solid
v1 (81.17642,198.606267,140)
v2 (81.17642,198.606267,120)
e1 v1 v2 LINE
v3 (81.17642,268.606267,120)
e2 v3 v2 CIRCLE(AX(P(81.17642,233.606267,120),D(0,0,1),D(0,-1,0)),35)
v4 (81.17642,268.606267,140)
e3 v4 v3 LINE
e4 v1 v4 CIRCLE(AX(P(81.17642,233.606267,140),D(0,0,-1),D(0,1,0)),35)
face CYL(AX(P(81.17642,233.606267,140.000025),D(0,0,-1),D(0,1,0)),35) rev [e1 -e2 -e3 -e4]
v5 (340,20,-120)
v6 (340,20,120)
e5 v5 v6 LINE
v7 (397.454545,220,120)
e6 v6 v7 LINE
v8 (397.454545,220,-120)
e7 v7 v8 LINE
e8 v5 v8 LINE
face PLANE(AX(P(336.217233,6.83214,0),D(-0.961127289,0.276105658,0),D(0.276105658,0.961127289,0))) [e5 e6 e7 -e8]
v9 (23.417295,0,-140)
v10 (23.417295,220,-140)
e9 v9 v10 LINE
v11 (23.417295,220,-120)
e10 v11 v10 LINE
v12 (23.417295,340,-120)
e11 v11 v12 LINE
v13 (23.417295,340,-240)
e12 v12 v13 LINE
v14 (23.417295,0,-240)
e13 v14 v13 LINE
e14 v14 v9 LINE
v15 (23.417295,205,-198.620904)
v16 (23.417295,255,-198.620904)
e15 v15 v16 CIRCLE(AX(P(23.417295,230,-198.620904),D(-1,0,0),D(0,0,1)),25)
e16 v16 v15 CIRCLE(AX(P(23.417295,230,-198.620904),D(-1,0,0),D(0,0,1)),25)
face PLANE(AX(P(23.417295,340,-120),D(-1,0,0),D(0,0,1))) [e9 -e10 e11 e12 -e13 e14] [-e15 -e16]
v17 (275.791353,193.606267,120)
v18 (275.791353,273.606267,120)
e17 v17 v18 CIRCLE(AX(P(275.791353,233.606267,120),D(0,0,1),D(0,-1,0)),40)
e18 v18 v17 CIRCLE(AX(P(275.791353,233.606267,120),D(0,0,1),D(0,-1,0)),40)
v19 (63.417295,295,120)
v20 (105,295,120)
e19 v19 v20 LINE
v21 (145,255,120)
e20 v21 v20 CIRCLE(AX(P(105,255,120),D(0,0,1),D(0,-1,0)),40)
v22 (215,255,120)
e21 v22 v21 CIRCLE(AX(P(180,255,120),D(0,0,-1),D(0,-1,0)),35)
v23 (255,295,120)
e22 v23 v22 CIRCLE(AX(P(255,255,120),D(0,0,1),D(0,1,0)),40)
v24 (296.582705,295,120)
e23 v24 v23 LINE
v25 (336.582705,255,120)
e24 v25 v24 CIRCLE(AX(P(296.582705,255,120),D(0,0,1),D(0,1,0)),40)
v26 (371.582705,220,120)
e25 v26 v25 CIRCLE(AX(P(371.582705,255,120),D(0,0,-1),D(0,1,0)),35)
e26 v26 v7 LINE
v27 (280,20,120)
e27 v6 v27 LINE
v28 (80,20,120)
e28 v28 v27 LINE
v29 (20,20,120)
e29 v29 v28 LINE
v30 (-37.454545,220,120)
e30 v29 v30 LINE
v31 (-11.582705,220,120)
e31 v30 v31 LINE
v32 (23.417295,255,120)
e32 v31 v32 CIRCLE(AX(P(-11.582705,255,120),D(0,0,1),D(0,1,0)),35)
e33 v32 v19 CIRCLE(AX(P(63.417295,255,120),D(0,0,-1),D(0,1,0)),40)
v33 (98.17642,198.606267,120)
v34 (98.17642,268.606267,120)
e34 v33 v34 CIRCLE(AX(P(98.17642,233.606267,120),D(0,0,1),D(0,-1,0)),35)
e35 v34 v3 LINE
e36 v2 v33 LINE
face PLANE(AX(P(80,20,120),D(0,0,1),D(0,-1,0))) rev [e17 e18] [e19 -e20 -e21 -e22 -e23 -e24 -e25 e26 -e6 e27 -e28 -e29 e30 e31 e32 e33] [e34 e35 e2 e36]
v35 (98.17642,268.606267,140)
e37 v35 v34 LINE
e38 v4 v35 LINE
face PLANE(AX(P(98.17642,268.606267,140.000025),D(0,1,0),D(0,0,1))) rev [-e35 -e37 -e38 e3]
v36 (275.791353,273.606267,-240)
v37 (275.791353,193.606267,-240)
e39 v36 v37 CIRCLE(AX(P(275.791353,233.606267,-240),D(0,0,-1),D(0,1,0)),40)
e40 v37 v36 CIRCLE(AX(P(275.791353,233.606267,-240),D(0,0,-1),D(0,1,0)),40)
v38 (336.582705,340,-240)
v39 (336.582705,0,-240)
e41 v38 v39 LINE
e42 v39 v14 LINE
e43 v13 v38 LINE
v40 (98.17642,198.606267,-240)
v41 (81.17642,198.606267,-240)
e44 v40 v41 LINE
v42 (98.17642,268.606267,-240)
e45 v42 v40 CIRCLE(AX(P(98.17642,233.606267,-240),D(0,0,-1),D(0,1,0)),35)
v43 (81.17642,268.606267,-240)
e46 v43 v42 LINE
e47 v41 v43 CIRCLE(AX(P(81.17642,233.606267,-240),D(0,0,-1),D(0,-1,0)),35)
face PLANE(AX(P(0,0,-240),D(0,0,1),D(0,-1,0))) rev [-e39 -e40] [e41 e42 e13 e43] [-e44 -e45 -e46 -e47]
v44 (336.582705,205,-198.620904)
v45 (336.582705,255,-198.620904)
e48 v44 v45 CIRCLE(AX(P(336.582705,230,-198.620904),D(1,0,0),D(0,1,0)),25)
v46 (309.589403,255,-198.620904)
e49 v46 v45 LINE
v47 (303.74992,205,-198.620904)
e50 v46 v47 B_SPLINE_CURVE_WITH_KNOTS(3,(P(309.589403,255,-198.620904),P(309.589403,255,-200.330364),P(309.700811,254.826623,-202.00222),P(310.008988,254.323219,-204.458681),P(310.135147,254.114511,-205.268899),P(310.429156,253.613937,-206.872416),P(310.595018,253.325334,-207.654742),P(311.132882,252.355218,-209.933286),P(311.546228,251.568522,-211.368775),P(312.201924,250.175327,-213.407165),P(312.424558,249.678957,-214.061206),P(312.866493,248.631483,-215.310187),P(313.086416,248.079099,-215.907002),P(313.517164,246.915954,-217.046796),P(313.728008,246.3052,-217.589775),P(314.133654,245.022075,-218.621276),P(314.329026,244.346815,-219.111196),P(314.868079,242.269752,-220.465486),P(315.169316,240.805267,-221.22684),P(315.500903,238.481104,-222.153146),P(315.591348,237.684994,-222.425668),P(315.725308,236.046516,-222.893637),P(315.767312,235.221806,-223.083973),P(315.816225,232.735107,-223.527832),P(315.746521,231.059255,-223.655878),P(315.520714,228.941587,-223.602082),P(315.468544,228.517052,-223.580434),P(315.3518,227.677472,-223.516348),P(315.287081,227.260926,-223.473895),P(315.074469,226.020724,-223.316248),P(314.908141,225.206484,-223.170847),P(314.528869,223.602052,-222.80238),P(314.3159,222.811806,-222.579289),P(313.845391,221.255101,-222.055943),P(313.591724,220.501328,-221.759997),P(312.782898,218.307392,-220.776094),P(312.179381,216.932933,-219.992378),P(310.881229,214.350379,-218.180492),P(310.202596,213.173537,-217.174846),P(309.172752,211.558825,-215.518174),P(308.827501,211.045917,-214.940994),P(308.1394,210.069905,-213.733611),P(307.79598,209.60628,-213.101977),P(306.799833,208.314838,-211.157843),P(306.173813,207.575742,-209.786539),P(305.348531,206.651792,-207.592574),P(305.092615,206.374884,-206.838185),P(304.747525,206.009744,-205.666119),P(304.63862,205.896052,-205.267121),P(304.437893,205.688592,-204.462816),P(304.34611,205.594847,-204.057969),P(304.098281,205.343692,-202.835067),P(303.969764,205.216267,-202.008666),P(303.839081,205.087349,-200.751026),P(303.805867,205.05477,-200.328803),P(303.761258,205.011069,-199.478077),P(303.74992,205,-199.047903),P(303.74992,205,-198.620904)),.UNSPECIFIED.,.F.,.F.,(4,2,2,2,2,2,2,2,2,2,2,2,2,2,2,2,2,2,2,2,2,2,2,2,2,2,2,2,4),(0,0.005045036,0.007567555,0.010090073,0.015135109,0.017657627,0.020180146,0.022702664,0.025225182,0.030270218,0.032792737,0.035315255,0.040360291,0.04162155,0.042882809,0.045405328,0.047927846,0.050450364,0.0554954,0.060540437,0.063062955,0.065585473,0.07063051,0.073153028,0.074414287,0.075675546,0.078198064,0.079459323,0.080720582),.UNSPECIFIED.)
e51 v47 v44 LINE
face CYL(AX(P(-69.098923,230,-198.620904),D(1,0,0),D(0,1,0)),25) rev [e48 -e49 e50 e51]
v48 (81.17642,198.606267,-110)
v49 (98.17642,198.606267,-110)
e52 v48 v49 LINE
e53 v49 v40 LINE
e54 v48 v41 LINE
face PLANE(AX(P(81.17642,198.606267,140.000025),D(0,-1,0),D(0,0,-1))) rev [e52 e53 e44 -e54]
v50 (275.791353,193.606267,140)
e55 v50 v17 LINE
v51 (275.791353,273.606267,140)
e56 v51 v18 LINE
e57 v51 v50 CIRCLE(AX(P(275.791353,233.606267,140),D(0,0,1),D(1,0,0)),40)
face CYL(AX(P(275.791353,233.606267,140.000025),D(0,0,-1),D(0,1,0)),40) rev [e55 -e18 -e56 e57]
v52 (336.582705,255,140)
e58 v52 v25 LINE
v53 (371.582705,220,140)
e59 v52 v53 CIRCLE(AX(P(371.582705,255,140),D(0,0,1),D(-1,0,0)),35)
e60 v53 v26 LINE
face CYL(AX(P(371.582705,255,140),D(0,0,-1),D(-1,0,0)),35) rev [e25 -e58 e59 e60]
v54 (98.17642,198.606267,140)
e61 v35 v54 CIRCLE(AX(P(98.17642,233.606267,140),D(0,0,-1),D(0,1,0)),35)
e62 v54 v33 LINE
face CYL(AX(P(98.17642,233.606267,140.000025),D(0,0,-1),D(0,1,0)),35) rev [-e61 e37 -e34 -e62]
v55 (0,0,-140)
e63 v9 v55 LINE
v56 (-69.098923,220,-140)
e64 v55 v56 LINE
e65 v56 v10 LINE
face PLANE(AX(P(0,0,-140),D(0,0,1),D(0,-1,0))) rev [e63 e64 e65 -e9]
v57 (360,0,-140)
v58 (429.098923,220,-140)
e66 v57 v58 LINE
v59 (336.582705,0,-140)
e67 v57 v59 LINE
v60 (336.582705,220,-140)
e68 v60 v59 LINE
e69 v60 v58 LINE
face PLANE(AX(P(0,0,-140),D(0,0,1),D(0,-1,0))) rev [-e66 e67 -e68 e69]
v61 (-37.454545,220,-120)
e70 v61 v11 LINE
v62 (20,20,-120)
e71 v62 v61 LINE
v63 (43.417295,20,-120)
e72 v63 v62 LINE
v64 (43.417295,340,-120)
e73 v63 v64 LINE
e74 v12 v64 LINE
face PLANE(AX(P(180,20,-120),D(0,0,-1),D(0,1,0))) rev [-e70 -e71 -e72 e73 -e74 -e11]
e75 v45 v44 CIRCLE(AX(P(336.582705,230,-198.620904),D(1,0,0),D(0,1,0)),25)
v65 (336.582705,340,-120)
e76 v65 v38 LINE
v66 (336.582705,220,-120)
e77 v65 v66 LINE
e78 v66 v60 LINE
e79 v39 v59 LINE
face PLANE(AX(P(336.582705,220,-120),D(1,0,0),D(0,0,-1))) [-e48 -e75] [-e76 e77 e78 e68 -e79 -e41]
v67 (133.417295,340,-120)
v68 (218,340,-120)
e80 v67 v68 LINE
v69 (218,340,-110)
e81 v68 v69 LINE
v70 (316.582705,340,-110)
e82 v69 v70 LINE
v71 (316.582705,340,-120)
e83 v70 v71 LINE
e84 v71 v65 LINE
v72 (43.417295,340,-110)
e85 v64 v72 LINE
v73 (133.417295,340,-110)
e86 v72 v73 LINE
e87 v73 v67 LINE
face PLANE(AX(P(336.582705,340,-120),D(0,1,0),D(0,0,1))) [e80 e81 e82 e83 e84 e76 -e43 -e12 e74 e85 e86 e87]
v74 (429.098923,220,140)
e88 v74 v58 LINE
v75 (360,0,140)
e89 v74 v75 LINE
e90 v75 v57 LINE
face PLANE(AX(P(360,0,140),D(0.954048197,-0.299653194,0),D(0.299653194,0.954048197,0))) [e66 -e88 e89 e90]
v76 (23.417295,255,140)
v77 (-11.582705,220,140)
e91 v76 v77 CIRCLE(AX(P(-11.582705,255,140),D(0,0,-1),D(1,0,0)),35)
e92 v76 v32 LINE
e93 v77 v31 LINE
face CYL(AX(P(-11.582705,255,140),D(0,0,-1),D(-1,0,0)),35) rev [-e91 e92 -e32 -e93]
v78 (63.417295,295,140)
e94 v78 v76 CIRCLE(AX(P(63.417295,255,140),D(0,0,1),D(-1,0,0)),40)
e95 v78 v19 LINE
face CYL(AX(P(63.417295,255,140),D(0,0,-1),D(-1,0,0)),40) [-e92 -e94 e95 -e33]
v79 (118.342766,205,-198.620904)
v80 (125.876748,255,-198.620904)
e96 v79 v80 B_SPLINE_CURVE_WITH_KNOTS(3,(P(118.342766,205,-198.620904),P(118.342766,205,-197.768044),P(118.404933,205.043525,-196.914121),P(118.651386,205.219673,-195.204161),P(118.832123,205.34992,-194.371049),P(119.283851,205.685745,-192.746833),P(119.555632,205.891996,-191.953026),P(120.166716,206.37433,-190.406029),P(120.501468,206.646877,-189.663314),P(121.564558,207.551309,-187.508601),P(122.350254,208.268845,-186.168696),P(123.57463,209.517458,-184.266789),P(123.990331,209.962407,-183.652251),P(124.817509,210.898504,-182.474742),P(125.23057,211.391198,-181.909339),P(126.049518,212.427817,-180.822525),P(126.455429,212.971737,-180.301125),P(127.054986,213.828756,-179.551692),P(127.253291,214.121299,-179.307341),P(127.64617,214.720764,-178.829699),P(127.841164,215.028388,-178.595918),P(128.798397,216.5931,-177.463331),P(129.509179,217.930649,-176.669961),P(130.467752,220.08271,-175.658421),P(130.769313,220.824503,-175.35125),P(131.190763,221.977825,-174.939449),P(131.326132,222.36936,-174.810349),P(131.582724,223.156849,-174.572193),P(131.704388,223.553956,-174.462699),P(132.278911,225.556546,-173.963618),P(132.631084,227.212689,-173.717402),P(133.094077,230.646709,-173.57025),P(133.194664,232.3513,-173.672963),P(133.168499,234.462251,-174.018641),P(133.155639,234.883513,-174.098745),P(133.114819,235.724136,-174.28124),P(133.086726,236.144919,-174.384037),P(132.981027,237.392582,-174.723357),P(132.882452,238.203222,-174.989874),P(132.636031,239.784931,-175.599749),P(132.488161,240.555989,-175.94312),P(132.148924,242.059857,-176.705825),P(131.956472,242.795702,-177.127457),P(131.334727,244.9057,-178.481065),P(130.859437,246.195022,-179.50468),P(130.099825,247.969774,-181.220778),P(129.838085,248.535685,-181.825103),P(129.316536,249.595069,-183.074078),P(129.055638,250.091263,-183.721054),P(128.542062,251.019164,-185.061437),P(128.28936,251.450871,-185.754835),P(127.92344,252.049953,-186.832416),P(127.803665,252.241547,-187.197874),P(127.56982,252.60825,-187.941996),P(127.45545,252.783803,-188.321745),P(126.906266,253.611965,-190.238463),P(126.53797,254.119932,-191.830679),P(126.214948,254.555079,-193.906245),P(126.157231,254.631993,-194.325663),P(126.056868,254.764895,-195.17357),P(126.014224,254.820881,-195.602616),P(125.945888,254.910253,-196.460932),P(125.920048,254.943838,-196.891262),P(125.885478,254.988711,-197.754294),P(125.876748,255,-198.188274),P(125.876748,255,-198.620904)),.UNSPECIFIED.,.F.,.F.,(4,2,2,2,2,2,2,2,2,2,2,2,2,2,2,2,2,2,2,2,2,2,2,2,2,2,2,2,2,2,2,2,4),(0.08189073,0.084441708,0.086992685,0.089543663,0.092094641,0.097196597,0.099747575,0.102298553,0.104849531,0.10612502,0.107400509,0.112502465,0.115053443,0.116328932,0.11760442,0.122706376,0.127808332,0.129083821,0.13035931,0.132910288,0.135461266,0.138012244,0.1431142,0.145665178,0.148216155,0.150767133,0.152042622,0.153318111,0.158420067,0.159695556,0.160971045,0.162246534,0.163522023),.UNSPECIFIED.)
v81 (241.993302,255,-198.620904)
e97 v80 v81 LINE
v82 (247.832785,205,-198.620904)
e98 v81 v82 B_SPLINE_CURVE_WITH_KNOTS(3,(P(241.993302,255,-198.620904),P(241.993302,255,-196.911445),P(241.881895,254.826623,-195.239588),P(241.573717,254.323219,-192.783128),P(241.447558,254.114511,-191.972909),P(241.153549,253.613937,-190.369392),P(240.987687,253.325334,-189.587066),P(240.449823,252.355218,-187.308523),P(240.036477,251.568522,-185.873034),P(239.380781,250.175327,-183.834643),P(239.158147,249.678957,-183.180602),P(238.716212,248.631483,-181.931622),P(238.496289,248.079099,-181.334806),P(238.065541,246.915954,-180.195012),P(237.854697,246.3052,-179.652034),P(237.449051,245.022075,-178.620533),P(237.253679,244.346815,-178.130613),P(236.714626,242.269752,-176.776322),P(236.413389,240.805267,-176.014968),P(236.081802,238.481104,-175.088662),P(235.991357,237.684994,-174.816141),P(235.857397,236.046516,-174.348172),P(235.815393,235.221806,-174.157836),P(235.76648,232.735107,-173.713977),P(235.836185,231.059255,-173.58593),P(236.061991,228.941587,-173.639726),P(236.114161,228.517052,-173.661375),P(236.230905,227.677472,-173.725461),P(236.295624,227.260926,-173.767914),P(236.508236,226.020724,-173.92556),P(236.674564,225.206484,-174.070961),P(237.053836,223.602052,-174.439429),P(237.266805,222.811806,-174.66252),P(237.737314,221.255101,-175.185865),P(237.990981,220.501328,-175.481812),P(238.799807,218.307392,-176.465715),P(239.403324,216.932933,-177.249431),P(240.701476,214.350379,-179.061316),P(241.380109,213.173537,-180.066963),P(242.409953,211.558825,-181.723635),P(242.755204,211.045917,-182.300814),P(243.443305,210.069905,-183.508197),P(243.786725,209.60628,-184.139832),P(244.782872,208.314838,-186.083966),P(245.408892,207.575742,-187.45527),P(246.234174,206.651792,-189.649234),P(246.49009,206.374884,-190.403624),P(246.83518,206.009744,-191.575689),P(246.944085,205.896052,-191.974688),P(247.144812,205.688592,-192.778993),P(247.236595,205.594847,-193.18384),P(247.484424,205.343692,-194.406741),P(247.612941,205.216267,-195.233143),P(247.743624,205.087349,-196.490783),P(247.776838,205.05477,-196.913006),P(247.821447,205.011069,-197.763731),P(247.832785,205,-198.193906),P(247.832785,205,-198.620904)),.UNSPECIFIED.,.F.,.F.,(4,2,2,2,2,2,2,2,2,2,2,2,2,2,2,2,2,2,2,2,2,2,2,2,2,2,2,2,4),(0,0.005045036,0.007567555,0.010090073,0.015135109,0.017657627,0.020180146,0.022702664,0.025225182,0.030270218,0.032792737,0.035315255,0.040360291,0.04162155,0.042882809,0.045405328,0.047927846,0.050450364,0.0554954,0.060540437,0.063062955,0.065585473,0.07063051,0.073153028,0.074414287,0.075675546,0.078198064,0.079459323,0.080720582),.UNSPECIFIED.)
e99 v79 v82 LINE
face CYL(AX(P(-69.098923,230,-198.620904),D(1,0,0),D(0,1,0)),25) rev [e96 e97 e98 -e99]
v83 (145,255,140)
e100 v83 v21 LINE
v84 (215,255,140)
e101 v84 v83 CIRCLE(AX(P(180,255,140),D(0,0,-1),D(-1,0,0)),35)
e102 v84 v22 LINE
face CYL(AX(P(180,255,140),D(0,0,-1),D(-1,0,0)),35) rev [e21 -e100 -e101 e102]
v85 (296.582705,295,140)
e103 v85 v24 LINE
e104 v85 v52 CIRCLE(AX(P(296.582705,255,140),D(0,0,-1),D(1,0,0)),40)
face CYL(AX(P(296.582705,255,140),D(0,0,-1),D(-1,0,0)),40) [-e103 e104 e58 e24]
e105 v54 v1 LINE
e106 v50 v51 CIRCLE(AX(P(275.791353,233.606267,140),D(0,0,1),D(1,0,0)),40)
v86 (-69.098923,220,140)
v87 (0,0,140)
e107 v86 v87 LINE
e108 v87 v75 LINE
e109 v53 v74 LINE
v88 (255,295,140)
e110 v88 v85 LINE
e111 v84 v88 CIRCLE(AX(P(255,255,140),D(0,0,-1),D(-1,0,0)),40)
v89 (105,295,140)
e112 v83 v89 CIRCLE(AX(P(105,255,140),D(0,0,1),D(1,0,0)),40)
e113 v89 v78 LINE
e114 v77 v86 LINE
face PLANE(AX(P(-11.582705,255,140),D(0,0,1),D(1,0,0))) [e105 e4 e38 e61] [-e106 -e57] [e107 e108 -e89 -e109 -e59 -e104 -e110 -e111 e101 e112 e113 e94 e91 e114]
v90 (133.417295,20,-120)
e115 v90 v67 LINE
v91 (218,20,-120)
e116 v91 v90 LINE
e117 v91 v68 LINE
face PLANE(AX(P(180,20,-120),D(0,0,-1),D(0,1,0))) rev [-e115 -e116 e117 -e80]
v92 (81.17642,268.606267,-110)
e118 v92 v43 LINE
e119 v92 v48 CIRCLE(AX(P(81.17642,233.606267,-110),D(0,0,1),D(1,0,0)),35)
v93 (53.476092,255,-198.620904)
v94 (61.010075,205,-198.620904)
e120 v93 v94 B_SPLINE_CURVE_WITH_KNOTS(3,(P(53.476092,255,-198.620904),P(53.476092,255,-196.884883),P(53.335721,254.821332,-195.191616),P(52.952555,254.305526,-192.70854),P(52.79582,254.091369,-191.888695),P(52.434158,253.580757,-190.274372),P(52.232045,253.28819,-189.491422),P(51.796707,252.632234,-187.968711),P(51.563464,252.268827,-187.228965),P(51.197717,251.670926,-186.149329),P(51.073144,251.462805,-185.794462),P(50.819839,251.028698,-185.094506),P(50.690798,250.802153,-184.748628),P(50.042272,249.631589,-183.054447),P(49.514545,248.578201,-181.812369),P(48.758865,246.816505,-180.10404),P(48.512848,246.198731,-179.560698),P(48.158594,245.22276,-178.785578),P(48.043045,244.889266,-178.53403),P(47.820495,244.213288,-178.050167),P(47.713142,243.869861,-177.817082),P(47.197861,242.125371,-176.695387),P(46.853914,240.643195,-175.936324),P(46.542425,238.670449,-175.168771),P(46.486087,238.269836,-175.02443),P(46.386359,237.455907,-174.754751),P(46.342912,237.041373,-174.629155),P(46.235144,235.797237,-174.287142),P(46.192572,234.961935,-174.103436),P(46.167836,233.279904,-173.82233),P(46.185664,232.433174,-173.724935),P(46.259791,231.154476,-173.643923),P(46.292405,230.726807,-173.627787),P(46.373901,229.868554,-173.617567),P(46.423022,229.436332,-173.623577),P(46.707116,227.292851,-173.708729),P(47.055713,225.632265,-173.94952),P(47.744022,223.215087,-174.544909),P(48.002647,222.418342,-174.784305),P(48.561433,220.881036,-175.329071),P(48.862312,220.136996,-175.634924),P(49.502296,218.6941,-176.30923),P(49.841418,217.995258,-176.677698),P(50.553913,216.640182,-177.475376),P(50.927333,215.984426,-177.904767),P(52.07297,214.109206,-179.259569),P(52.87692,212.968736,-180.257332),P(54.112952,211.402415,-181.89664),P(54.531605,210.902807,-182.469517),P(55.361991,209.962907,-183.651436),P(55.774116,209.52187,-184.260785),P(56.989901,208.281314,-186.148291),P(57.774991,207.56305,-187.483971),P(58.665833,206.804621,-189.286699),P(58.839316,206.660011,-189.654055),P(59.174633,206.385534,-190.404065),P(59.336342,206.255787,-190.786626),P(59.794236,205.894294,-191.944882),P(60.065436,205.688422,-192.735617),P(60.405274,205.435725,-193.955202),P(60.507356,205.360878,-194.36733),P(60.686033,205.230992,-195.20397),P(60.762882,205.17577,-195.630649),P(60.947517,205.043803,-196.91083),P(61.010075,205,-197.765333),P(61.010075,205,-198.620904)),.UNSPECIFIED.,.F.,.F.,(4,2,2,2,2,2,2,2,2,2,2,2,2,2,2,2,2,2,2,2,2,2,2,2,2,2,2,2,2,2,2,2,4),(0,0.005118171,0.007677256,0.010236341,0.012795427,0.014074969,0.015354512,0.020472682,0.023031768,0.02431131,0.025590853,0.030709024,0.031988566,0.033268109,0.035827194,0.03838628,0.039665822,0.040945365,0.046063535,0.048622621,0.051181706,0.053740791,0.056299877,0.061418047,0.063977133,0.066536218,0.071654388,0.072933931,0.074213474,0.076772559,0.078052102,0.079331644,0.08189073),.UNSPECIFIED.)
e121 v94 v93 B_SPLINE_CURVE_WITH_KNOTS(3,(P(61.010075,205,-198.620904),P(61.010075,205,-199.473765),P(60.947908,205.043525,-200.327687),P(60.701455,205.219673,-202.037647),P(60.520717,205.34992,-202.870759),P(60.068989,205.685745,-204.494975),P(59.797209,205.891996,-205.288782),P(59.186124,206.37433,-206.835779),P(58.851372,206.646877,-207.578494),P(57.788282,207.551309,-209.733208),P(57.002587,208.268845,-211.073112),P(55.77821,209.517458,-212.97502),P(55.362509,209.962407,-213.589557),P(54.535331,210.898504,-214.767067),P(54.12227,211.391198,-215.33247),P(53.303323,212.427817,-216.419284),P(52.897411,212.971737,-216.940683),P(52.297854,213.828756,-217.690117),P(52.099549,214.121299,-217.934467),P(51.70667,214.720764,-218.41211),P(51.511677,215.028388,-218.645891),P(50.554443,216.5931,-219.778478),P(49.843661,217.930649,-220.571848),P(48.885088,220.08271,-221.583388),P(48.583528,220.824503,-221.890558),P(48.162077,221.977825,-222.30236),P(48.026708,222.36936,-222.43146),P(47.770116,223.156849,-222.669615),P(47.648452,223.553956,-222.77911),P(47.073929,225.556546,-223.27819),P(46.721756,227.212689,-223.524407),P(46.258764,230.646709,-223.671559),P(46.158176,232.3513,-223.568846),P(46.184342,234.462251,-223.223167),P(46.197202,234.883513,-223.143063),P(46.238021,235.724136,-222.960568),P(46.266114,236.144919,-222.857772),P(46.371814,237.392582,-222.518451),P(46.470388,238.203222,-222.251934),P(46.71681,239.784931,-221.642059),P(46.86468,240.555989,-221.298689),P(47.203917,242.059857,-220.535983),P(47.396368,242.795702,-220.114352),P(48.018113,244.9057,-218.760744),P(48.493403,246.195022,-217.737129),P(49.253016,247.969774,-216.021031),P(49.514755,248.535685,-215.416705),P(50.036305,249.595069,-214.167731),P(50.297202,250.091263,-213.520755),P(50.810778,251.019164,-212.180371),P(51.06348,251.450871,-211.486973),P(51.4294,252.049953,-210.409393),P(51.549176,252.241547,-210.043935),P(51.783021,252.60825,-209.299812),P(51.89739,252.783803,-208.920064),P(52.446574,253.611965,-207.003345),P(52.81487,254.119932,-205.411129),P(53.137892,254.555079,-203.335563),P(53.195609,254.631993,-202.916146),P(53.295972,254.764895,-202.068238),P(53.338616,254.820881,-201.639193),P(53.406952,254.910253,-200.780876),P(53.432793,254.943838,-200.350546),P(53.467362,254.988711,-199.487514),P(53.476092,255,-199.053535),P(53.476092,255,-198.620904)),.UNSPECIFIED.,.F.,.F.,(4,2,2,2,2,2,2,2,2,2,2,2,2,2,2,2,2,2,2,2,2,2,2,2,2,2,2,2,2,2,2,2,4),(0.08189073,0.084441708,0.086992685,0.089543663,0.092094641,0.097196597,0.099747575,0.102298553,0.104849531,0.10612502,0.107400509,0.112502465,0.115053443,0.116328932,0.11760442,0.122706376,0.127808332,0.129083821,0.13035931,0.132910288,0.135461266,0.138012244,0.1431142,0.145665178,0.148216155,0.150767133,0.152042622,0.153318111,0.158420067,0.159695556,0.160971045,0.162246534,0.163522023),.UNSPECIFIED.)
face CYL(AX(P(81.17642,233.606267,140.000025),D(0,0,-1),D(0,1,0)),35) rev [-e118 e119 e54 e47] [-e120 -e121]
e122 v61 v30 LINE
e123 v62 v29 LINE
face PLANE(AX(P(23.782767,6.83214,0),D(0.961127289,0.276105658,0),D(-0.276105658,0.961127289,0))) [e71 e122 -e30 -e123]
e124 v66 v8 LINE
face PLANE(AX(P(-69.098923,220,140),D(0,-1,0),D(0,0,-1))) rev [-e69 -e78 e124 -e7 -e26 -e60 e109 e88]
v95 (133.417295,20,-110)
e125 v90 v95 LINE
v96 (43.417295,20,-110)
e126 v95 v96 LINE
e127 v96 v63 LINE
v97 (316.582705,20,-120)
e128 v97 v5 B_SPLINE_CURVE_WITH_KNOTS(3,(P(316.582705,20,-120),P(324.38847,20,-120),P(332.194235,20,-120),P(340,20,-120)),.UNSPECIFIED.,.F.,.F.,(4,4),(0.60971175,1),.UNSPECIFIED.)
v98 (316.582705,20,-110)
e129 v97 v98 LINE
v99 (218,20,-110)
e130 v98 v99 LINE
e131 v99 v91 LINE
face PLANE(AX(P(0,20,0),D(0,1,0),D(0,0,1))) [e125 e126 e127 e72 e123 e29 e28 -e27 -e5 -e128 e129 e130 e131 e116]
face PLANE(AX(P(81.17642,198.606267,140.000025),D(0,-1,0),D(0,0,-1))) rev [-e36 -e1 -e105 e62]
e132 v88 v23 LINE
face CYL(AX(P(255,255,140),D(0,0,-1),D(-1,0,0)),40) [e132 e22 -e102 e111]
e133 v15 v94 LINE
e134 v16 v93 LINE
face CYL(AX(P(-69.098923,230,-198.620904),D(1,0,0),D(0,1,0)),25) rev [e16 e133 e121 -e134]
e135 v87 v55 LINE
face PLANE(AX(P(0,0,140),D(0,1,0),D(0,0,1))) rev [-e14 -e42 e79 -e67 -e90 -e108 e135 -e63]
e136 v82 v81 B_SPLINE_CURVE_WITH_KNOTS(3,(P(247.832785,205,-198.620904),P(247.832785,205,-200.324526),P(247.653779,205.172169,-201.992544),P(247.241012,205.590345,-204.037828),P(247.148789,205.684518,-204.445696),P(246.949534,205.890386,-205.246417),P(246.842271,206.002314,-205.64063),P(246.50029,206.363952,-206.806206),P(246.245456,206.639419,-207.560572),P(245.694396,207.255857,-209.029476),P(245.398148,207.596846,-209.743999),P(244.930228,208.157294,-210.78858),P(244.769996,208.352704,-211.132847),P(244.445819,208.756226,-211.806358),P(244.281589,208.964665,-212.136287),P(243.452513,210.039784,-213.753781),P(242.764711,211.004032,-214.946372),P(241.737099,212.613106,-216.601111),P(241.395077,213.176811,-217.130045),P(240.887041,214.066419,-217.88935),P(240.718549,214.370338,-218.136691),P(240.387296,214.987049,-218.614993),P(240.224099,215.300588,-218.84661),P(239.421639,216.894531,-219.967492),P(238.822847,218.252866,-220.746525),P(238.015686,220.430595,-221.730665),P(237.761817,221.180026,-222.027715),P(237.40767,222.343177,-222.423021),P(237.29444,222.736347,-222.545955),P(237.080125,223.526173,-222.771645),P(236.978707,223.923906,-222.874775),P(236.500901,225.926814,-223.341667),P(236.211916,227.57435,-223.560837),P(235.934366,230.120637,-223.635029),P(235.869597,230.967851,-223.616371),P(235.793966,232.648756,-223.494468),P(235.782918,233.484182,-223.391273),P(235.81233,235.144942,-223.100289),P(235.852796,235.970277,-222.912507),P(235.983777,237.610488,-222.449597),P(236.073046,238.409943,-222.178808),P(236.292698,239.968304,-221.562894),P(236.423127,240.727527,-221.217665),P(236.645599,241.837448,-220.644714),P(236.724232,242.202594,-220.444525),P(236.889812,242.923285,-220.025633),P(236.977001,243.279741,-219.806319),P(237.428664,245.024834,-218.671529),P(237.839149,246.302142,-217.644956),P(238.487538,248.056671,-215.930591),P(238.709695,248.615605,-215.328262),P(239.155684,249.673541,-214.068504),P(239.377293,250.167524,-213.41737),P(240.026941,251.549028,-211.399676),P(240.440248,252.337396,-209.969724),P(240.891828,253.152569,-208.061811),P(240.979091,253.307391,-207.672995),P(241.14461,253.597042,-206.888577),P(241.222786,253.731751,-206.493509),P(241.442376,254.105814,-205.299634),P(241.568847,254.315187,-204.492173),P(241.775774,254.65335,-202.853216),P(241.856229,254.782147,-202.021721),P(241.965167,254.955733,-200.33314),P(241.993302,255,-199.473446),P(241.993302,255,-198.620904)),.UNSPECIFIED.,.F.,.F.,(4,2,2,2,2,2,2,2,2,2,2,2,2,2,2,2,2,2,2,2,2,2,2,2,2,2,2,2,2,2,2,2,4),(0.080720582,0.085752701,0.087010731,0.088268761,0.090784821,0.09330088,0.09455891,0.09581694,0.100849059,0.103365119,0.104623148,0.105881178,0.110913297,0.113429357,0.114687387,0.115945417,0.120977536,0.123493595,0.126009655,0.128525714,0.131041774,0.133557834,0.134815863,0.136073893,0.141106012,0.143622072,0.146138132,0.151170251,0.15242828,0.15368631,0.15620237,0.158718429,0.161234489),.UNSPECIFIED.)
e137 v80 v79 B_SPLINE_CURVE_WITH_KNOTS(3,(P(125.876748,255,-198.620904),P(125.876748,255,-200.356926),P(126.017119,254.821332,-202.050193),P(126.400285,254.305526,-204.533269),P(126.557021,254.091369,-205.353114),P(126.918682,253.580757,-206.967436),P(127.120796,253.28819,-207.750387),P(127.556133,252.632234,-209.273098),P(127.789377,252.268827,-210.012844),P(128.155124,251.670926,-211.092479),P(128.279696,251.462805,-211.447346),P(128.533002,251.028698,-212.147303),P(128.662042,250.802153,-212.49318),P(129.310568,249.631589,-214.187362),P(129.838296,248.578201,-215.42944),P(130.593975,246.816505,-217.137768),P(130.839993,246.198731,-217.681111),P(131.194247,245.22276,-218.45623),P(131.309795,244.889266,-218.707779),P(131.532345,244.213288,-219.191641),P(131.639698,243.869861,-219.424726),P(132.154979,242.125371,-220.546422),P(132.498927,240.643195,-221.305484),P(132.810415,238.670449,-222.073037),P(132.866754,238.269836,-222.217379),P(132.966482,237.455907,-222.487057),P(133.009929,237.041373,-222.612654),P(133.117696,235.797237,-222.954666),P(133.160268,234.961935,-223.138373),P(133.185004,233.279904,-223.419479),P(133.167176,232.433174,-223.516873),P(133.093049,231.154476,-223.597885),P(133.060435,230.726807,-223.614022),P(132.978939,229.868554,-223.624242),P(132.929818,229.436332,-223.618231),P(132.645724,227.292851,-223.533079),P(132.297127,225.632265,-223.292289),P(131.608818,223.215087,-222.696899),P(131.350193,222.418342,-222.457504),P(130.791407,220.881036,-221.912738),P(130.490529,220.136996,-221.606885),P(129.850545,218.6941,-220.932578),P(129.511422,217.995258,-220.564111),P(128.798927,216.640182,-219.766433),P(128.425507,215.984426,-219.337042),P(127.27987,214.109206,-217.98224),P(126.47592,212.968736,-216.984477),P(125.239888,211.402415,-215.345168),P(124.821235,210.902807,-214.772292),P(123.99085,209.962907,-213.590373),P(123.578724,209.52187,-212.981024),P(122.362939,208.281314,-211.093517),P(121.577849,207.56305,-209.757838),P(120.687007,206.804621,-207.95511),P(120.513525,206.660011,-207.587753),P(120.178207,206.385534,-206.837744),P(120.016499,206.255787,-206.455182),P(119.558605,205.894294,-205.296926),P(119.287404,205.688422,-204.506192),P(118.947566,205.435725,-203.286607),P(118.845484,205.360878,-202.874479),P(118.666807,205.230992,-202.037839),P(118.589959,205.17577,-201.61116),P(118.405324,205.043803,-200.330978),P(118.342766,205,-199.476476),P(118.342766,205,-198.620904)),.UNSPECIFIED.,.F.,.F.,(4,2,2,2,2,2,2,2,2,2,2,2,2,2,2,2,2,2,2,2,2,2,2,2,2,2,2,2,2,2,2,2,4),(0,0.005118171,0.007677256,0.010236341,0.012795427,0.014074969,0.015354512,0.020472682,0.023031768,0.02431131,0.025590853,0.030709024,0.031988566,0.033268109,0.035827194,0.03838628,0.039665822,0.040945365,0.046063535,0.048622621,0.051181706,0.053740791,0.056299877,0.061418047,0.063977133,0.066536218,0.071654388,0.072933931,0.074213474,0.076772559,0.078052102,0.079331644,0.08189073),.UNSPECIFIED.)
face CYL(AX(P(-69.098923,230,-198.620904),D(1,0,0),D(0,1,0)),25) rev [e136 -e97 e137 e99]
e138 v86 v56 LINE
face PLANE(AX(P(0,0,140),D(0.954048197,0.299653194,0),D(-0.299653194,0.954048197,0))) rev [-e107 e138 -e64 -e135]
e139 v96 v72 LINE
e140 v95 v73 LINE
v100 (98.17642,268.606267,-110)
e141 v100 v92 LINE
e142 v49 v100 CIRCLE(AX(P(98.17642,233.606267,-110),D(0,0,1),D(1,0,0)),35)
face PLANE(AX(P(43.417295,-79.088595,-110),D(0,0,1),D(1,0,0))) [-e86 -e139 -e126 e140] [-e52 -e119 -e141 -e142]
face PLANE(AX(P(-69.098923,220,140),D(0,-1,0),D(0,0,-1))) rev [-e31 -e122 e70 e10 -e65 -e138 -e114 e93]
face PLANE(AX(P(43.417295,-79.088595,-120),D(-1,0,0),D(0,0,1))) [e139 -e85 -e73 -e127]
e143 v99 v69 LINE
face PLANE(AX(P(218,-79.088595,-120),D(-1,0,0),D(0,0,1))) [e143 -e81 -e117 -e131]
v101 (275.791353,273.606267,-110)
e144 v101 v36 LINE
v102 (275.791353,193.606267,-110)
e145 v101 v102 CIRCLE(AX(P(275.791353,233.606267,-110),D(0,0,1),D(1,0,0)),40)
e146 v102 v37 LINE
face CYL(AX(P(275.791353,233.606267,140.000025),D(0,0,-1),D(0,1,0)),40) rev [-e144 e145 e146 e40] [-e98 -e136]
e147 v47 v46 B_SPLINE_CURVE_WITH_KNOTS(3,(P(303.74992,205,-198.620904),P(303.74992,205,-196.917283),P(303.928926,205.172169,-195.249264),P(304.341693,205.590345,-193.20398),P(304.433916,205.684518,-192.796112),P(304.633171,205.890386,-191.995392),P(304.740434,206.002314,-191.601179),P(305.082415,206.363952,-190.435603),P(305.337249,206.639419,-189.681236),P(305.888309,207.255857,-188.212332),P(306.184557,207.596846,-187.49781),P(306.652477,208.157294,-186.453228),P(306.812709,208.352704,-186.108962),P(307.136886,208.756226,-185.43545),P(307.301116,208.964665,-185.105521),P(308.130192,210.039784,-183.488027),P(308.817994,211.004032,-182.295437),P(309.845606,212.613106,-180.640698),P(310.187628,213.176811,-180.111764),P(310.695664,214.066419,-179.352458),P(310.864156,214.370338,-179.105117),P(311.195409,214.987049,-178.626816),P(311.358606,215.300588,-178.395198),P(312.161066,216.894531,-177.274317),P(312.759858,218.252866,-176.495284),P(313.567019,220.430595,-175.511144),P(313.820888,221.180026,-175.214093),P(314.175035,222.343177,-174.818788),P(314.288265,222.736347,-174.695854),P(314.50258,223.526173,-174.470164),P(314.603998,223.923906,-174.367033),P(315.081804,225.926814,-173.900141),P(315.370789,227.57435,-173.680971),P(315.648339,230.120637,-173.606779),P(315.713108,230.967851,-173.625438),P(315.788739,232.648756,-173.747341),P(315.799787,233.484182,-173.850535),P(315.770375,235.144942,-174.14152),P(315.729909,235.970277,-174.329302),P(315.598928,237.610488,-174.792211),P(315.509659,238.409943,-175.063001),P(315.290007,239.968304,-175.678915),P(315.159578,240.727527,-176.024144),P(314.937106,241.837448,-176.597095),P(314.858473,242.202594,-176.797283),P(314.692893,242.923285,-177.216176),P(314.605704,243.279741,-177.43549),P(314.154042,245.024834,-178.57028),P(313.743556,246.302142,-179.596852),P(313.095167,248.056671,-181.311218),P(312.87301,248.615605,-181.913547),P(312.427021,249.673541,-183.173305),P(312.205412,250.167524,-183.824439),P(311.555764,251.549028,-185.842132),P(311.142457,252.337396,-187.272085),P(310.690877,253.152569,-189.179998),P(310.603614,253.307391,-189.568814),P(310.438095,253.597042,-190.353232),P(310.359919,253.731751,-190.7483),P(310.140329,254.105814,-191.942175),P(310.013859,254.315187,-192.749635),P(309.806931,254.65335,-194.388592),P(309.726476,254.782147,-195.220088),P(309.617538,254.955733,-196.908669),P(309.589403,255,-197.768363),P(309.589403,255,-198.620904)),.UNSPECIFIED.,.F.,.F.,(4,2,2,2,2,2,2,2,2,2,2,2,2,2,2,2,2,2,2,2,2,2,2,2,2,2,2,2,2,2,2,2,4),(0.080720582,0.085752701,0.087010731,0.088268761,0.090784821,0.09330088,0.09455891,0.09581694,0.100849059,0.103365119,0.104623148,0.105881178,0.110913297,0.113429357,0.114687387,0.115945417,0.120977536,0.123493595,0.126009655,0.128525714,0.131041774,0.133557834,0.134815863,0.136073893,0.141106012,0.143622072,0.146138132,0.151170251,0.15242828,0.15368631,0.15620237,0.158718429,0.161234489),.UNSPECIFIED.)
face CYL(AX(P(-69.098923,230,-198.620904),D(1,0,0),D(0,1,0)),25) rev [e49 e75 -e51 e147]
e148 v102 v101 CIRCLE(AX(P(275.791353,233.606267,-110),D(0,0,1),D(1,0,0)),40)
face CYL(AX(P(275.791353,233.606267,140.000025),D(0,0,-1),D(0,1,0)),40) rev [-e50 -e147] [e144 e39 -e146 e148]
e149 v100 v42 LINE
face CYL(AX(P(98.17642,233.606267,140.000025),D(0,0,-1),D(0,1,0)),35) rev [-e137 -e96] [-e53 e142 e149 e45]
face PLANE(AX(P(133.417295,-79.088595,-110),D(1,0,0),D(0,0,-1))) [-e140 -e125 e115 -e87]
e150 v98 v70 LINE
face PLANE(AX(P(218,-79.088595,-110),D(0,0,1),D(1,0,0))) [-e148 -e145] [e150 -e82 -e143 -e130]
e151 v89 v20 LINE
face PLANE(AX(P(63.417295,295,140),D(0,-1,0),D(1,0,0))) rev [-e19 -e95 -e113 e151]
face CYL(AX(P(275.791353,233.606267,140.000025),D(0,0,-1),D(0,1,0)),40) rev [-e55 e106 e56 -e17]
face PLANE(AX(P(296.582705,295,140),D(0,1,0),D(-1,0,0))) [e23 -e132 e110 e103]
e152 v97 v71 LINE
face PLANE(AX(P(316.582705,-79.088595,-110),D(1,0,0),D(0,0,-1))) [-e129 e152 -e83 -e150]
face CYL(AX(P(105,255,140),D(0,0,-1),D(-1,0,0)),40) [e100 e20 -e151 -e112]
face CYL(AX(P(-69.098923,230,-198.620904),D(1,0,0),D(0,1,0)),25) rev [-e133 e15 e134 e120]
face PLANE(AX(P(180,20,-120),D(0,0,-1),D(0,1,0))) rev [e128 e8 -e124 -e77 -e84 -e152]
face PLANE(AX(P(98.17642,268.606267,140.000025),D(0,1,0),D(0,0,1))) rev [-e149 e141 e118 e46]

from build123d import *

# Parameters (mm, degrees)
EXTRUDE_2_DEPTH          = 140
EXTRUDE_3_DEPTH          = 140
SKETCH_8_W               = 100
SKETCH_8_H               = 240
CUT_EXTRUDE_1_DEPTH      = 275
EXTRUDE_4_DEPTH          = 100
EXTRUDE_4_DEPTH_BACK     = 20
SKETCH_12_W              = 313.16541006
SKETCH_12_H              = 120
SKETCH_13_W              = 313.16541006
SKETCH_13_H              = 220
EXTRUDE_5_DEPTH          = 100
SKETCH_14_R              = 25
CUT_EXTRUDE_2_DEPTH      = 582.186358517
SKETCH_15_W              = 90
SKETCH_15_H              = 10
SKETCH_15_W_2            = 98.58270503
EXTRUDE_6_DEPTH          = 320
CUT_EXTRUDE_3_DEPTH      = 615.919414052
CUT_EXTRUDE_3_DEPTH_BACK = 615.919414052
SKETCH_16_R              = 40


with BuildPart() as part:
    # 草图1 → 凸台-拉伸2 (new body)
    with BuildSketch(Plane.XY):
        with BuildLine():
            Line((0, 0), (180, 0))
            Line((180, 0), (180, 220))
            ThreePointArc((180, 220), (155.251262658, 230.251262658), (145, 255))
            ThreePointArc((145, 255), (133.284271247, 283.284271247), (105, 295))
            Line((105, 295), (63.41729497, 295))
            ThreePointArc((63.41729497, 295), (35.133023723, 283.284271247), (23.41729497, 255))
            ThreePointArc((23.41729497, 255), (13.166032312, 230.251262658), (-11.58270503, 220))
            Line((-11.58270503, 220), (-69.098922823, 220))
            Line((-69.098922823, 220), (0, 0))
        make_face()
    extrude_2 = extrude(amount=EXTRUDE_2_DEPTH)

    # 草图5 → 凸台-拉伸3 (add)
    with BuildSketch(Plane(origin=(0, 0, 0), x_dir=(-1, 0, 0), z_dir=(0, 0, -1))):
        Polygon((-180, 220), (69.098922823, 220), (0, 0), (-180, 0), align=None)
    extrude_3 = extrude(amount=EXTRUDE_3_DEPTH)

    # 草图8 → 切除-拉伸1 (cut)
    with BuildSketch(Plane(origin=(0, 295, 0), x_dir=(1, 0, 0), z_dir=(0, 1, 0))):
        with Locations((130, 0)):
            Rectangle(SKETCH_8_W, SKETCH_8_H)
    cut_extrude_1 = extrude(amount=-CUT_EXTRUDE_1_DEPTH, mode=Mode.SUBTRACT)

    # 草图10 → 切除-放样4 section 0
    with BuildSketch(Plane(origin=(0, 20, 0), x_dir=(1, 0, 0), z_dir=(0, 1, 0))):
        with BuildLine():
            Line((80, 120), (20, 120))
            Line((20, 120), (20, -120))
            Line((20, -120), (80, -120))
            Line((80, -120), (80, 120))
        make_face()
    # 草图11 → 切除-放样4 section 1
    with BuildSketch(Plane(origin=(0, 295, 0), x_dir=(1, 0, 0), z_dir=(0, 1, 0))):
        with BuildLine():
            Line((80, 120), (80, -120))
            Line((80, -120), (-59, -120))
            Line((-59, -120), (-59, 120))
            Line((-59, 120), (80, 120))
        make_face()
    loft_4 = loft(mode=Mode.SUBTRACT)

    # 镜向1: 凸台-拉伸2, 凸台-拉伸3, 切除-拉伸1, 切除-放样4 across plane
    add(extrude_2.mirror(Plane(origin=(180, 0, 140), x_dir=(0, 0, 1), z_dir=(-1, 0, 0))))
    add(extrude_3.mirror(Plane(origin=(180, 0, 140), x_dir=(0, 0, 1), z_dir=(-1, 0, 0))))
    add(cut_extrude_1.mirror(Plane(origin=(180, 0, 140), x_dir=(0, 0, 1), z_dir=(-1, 0, 0))), mode=Mode.SUBTRACT)
    add(loft_4.mirror(Plane(origin=(180, 0, 140), x_dir=(0, 0, 1), z_dir=(-1, 0, 0))), mode=Mode.SUBTRACT)

    # 草图12 → 凸台-拉伸4 (add, two sides: drawn at the far end of the back side and taken through both)
    with BuildSketch(Plane(origin=(0, 0, -140), x_dir=(-1, 0, 0), z_dir=(0, 0, -1)).offset(-EXTRUDE_4_DEPTH_BACK)):
        with Locations((-180, 280)):
            Rectangle(SKETCH_12_W, SKETCH_12_H)
    extrude(amount=EXTRUDE_4_DEPTH + EXTRUDE_4_DEPTH_BACK)

    # 草图13 → 凸台-拉伸5 (add)
    with BuildSketch(Plane(origin=(0, 0, -140), x_dir=(-1, 0, 0), z_dir=(0, 0, -1))):
        with Locations((-180, 110)):
            Rectangle(SKETCH_13_W, SKETCH_13_H)
    extrude(amount=EXTRUDE_5_DEPTH)

    # 草图14 → 切除-拉伸2 (cut, through all)
    with BuildSketch(Plane(origin=(336.58270503, 0, 0), x_dir=(0, 0, -1), z_dir=(1, 0, 0))):
        with Locations(Location((198.620904307, 230, 0), (0, 0, 90))):
            Circle(SKETCH_14_R)
    extrude(amount=-CUT_EXTRUDE_2_DEPTH, mode=Mode.SUBTRACT)

    # 草图15 → 凸台-拉伸6 (add)
    with BuildSketch(Plane(origin=(0, 340, 0), x_dir=(1, 0, 0), z_dir=(0, 1, 0))):
        with Locations((88.41729497, 115)):
            Rectangle(SKETCH_15_W, SKETCH_15_H)
        with Locations((267.291352515, 115)):
            Rectangle(SKETCH_15_W_2, SKETCH_15_H)
    extrude(amount=-EXTRUDE_6_DEPTH)

    # 草图16 → 切除-拉伸3 (cut, two sides: drawn at the far end of the back side and taken through both)
    with BuildSketch(Plane(origin=(0, 0, -140), x_dir=(-1, 0, 0), z_dir=(0, 0, -1)).offset(-CUT_EXTRUDE_3_DEPTH_BACK)):
        with Locations(Location((-275.791352515, 233.606267036, 0), (0, 0, 90))):
            Circle(SKETCH_16_R)
        with BuildLine():
            Line((-98.176420136, 268.606267036), (-81.17642014, 268.606267036))
            ThreePointArc((-81.17642014, 268.606267036), (-46.17642014, 233.606267036), (-81.17642014, 198.606267036))
            Line((-81.17642014, 198.606267036), (-98.176420136, 198.606267036))
            ThreePointArc((-98.176420136, 198.606267036), (-133.176420136, 233.606267036), (-98.176420136, 268.606267036))
        make_face()
    extrude(amount=CUT_EXTRUDE_3_DEPTH + CUT_EXTRUDE_3_DEPTH_BACK, mode=Mode.SUBTRACT)


solid = part.part
